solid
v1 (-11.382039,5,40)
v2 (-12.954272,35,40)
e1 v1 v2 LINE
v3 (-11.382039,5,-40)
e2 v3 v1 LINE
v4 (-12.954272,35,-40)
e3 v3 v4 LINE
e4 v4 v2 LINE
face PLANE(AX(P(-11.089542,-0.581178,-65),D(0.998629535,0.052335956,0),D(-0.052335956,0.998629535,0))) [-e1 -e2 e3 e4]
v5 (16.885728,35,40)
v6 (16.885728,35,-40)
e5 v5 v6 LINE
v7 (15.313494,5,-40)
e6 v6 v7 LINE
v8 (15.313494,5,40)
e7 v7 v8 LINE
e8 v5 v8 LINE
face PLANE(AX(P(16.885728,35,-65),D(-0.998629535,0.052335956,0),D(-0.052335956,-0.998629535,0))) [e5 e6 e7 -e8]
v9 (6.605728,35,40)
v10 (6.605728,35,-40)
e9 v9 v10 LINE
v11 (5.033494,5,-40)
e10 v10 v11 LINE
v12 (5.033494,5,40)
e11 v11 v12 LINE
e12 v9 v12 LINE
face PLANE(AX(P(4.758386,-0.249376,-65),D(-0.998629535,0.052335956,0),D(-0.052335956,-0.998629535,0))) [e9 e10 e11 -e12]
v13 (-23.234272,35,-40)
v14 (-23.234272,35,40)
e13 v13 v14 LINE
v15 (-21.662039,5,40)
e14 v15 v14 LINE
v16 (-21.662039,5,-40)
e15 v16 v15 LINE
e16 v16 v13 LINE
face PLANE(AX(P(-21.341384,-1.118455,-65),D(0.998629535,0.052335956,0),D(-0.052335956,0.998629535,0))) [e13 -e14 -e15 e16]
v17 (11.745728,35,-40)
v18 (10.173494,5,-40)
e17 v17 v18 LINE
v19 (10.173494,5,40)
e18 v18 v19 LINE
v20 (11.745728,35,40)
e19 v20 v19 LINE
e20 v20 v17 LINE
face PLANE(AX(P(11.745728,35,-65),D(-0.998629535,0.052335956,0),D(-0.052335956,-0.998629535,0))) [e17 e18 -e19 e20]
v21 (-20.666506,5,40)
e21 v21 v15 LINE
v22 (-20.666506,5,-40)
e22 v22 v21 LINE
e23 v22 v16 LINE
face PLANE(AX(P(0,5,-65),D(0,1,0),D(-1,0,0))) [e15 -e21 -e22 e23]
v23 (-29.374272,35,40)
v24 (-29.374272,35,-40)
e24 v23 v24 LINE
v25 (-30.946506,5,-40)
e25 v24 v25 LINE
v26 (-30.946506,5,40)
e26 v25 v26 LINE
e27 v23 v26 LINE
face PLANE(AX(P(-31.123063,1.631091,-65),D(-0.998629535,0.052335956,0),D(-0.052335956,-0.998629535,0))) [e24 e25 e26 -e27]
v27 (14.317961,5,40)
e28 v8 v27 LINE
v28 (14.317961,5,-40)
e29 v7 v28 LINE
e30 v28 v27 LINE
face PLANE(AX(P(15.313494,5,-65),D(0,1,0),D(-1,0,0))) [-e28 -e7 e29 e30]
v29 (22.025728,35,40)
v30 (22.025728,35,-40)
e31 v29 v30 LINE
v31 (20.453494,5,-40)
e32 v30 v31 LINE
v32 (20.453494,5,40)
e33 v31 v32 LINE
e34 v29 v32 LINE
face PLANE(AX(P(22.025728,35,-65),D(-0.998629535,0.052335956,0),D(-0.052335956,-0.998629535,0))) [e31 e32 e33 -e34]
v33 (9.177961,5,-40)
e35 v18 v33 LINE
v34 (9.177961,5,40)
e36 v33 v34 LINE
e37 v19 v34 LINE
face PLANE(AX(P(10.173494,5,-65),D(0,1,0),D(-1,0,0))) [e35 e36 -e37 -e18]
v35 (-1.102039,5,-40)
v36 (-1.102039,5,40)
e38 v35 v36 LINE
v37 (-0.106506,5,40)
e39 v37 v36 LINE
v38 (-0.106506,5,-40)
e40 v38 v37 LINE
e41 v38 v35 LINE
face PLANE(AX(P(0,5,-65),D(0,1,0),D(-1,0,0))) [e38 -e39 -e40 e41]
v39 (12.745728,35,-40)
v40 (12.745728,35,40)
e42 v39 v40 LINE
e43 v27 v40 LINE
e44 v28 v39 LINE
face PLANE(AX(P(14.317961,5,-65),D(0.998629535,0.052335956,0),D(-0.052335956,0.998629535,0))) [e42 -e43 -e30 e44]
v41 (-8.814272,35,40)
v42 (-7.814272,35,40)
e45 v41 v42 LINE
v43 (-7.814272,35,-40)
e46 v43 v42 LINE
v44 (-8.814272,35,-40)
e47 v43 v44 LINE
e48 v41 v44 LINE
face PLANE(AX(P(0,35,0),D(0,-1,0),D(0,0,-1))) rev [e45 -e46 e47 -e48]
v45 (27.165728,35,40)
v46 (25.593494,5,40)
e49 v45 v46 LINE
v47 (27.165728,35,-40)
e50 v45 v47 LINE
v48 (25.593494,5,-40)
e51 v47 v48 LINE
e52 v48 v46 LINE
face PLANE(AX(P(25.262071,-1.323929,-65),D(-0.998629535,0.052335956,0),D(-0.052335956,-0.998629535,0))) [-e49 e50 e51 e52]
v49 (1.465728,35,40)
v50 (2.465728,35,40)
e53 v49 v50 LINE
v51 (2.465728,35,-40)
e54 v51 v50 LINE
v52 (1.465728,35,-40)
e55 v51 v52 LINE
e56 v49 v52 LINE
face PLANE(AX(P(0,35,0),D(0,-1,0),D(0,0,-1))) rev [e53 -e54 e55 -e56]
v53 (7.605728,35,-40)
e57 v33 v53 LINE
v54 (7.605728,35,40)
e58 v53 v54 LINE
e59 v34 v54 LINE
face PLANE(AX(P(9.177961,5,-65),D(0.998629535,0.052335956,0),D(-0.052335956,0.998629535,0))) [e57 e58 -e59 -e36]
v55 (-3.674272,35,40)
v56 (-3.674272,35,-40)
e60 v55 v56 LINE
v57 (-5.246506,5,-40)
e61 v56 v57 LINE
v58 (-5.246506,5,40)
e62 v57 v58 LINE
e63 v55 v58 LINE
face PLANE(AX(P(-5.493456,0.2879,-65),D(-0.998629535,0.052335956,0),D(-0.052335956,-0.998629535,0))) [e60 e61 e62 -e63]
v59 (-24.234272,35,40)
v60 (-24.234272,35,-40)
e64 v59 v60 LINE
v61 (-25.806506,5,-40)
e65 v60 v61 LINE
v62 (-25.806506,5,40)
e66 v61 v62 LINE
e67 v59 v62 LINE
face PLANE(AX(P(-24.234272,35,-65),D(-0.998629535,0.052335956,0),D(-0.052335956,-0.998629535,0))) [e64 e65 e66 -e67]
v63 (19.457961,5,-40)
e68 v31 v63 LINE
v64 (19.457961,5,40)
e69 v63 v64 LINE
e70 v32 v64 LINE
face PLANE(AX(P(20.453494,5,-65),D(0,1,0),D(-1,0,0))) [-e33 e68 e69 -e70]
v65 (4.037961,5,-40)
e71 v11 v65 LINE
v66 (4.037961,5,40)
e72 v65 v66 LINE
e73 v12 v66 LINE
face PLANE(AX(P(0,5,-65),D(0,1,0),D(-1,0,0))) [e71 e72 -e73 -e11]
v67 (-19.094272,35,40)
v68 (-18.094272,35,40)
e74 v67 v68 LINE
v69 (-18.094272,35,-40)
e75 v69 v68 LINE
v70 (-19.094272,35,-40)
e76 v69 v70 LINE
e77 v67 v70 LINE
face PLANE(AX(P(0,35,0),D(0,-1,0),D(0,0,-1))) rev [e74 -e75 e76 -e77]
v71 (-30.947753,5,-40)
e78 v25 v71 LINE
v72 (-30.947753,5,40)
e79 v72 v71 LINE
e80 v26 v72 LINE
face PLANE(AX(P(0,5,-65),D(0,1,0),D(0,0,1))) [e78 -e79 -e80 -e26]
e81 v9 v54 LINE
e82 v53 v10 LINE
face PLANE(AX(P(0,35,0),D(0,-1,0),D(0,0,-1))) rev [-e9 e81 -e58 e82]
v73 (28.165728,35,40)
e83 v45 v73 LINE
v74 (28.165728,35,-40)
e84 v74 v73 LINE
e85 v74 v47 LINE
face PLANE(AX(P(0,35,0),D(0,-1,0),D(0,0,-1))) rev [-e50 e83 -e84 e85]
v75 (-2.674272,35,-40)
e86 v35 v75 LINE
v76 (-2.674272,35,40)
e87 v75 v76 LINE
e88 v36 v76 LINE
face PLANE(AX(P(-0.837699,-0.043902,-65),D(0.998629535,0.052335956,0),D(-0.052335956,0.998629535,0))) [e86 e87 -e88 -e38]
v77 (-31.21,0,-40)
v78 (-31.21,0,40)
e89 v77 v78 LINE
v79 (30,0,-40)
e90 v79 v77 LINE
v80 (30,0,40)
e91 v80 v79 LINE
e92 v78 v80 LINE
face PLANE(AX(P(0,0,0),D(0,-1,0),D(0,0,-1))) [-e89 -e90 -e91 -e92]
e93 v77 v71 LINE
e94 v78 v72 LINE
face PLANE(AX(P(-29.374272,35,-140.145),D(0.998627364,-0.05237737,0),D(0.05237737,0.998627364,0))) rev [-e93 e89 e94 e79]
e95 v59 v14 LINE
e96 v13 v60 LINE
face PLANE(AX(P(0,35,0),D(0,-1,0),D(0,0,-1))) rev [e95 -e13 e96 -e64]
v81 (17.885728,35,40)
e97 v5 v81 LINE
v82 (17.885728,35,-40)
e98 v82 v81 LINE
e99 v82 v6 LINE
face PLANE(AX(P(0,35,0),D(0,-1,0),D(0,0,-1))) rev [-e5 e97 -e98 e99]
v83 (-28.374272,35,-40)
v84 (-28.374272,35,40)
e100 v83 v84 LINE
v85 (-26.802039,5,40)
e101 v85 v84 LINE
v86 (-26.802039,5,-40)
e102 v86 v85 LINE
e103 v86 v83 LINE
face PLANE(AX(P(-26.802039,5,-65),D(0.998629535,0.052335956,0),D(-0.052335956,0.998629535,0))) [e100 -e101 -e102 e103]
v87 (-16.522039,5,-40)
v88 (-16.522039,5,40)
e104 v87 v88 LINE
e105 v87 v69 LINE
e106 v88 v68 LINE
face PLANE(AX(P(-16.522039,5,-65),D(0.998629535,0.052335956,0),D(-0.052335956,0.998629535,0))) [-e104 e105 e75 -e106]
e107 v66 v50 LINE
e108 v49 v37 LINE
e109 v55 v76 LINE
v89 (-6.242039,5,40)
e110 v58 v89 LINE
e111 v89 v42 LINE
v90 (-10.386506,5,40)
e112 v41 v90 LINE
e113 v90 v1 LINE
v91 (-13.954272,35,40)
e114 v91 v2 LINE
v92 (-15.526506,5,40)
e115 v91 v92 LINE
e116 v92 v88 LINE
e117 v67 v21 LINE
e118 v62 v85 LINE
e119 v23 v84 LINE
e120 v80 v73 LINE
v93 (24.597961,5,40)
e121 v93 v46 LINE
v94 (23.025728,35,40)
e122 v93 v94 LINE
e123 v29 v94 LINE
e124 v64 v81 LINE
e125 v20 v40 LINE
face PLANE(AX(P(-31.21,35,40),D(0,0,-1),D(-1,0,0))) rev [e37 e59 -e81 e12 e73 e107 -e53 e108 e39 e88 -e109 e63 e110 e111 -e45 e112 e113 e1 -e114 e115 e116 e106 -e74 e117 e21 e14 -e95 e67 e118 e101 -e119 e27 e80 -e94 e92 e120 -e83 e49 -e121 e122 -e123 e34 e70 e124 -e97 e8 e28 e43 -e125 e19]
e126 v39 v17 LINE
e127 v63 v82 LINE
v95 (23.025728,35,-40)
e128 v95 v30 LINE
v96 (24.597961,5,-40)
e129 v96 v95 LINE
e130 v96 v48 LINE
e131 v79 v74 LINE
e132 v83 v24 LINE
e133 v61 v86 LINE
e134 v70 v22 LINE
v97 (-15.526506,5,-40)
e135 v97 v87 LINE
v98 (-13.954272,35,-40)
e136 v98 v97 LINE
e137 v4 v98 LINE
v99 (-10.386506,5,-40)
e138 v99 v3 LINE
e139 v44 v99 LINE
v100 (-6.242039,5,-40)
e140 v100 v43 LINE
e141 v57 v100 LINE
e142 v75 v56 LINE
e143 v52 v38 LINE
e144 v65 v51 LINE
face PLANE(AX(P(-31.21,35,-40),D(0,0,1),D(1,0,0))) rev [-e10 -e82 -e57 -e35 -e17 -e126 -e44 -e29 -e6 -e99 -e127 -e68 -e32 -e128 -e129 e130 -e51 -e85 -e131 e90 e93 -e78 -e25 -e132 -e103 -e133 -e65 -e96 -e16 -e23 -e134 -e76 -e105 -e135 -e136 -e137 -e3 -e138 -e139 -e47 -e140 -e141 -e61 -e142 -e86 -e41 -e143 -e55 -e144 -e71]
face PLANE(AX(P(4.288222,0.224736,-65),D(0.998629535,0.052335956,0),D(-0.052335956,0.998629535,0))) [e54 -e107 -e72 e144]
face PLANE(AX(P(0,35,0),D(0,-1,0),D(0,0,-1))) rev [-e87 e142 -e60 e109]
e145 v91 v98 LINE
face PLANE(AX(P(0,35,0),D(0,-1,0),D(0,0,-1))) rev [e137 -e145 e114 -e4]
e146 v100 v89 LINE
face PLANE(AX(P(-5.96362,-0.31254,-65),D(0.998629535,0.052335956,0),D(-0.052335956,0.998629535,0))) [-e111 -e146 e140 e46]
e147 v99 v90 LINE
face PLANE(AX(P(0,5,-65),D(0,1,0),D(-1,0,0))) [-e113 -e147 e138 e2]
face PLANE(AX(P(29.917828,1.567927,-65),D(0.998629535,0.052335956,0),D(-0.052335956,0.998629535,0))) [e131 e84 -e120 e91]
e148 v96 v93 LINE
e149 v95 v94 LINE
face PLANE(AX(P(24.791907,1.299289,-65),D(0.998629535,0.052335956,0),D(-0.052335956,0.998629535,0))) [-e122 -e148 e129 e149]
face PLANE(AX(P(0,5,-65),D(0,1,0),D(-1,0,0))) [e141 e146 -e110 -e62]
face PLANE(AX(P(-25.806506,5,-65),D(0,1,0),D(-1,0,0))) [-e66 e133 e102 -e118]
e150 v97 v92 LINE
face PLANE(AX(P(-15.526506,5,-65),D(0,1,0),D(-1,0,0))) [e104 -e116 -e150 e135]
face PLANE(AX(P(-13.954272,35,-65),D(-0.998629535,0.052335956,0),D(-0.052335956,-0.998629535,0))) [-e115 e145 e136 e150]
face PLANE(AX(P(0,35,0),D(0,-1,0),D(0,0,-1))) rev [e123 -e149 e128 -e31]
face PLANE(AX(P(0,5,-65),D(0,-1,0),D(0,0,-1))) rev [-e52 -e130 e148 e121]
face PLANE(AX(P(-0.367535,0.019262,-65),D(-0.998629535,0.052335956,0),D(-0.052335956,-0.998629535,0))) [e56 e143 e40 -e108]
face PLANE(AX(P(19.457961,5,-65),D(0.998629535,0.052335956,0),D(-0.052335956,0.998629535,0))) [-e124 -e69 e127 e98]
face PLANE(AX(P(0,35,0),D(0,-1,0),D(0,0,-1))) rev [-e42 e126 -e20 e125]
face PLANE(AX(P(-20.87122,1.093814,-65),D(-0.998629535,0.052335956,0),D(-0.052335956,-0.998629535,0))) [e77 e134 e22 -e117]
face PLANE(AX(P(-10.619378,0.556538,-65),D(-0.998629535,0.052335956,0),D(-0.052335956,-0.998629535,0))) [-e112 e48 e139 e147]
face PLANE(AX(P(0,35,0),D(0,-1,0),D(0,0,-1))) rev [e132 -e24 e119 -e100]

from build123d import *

# Parameters (mm, degrees)
BASE_PROFILE_SKETCH_W      = 61.21
BASE_PROFILE_SKETCH_H      = 80
HEAT_SINK_BASE_BLOCK_DEPTH = 35
FIN_SLOTS_CUT_DEPTH        = 105
SIDE_TRIM_CUT_DEPTH        = 180.145


with BuildPart() as part:
    # Base Profile Sketch → Heat Sink Base Block (new body)
    with BuildSketch(Plane(origin=(0, 0, 0), x_dir=(1, 0, 0), z_dir=(0, 1, 0))):
        with Locations((-0.605, 0)):
            Rectangle(BASE_PROFILE_SKETCH_W, BASE_PROFILE_SKETCH_H)
    extrude(amount=HEAT_SINK_BASE_BLOCK_DEPTH)

    # Fin Slots Sketch → Fin Slots Cut (cut)
    with BuildSketch(Plane.XY.offset(40)):
        Polygon((23.025727725, 35), (24.597961104, 5), (25.593494347, 5), (27.165727725, 35), align=None)
        Polygon((28.165727725, 35), (30, 0), (30, 35), align=None)
        Polygon((20.453494347, 5), (22.025727725, 35), (22.021260968, 35), (17.885727725, 35), (19.457961104, 5), align=None)
        Polygon((15.313494347, 5), (16.885727725, 35), (12.745727725, 35), (14.317961104, 5), align=None)
        Polygon((10.173494347, 5), (11.745727725, 35), (7.605727725, 35), (9.177961104, 5), align=None)
        Polygon((5.033494347, 5), (6.605727725, 35), (2.465727725, 35), (4.037961104, 5), align=None)
        Polygon((-0.106505653, 5), (1.465727725, 35), (-2.674272275, 35), (-1.102038896, 5), align=None)
        Polygon((-5.246505653, 5), (-3.674272275, 35), (-7.814272275, 35), (-6.242038896, 5), align=None)
        Polygon((-10.386505653, 5), (-8.814272275, 35), (-12.954272275, 35), (-11.382038896, 5), align=None)
        Polygon((-15.526505653, 5), (-13.954272275, 35), (-18.094272275, 35), (-16.522038896, 5), align=None)
        Polygon((-20.666505653, 5), (-19.094272275, 35), (-23.234272275, 35), (-21.662038896, 5), align=None)
        Polygon((-25.806505653, 5), (-24.234272275, 35), (-28.374272275, 35), (-26.802038896, 5), align=None)
        Polygon((-30.946505653, 5), (-29.374272275, 35), (-31.20854455, 35), (-31.20854455, 5), align=None)
    extrude(amount=-FIN_SLOTS_CUT_DEPTH, mode=Mode.SUBTRACT)

    # Side Trim Sketch → Side Trim Cut (cut)
    with BuildSketch(Plane.XY.offset(40)):
        Polygon((-29.374272275, 35), (-31.21, 0), (-36.791681348, 0), (-36.791681348, 36.336825614), (-29.374272275, 36.336825614), align=None)
    extrude(amount=-SIDE_TRIM_CUT_DEPTH, mode=Mode.SUBTRACT)


solid = part.part
